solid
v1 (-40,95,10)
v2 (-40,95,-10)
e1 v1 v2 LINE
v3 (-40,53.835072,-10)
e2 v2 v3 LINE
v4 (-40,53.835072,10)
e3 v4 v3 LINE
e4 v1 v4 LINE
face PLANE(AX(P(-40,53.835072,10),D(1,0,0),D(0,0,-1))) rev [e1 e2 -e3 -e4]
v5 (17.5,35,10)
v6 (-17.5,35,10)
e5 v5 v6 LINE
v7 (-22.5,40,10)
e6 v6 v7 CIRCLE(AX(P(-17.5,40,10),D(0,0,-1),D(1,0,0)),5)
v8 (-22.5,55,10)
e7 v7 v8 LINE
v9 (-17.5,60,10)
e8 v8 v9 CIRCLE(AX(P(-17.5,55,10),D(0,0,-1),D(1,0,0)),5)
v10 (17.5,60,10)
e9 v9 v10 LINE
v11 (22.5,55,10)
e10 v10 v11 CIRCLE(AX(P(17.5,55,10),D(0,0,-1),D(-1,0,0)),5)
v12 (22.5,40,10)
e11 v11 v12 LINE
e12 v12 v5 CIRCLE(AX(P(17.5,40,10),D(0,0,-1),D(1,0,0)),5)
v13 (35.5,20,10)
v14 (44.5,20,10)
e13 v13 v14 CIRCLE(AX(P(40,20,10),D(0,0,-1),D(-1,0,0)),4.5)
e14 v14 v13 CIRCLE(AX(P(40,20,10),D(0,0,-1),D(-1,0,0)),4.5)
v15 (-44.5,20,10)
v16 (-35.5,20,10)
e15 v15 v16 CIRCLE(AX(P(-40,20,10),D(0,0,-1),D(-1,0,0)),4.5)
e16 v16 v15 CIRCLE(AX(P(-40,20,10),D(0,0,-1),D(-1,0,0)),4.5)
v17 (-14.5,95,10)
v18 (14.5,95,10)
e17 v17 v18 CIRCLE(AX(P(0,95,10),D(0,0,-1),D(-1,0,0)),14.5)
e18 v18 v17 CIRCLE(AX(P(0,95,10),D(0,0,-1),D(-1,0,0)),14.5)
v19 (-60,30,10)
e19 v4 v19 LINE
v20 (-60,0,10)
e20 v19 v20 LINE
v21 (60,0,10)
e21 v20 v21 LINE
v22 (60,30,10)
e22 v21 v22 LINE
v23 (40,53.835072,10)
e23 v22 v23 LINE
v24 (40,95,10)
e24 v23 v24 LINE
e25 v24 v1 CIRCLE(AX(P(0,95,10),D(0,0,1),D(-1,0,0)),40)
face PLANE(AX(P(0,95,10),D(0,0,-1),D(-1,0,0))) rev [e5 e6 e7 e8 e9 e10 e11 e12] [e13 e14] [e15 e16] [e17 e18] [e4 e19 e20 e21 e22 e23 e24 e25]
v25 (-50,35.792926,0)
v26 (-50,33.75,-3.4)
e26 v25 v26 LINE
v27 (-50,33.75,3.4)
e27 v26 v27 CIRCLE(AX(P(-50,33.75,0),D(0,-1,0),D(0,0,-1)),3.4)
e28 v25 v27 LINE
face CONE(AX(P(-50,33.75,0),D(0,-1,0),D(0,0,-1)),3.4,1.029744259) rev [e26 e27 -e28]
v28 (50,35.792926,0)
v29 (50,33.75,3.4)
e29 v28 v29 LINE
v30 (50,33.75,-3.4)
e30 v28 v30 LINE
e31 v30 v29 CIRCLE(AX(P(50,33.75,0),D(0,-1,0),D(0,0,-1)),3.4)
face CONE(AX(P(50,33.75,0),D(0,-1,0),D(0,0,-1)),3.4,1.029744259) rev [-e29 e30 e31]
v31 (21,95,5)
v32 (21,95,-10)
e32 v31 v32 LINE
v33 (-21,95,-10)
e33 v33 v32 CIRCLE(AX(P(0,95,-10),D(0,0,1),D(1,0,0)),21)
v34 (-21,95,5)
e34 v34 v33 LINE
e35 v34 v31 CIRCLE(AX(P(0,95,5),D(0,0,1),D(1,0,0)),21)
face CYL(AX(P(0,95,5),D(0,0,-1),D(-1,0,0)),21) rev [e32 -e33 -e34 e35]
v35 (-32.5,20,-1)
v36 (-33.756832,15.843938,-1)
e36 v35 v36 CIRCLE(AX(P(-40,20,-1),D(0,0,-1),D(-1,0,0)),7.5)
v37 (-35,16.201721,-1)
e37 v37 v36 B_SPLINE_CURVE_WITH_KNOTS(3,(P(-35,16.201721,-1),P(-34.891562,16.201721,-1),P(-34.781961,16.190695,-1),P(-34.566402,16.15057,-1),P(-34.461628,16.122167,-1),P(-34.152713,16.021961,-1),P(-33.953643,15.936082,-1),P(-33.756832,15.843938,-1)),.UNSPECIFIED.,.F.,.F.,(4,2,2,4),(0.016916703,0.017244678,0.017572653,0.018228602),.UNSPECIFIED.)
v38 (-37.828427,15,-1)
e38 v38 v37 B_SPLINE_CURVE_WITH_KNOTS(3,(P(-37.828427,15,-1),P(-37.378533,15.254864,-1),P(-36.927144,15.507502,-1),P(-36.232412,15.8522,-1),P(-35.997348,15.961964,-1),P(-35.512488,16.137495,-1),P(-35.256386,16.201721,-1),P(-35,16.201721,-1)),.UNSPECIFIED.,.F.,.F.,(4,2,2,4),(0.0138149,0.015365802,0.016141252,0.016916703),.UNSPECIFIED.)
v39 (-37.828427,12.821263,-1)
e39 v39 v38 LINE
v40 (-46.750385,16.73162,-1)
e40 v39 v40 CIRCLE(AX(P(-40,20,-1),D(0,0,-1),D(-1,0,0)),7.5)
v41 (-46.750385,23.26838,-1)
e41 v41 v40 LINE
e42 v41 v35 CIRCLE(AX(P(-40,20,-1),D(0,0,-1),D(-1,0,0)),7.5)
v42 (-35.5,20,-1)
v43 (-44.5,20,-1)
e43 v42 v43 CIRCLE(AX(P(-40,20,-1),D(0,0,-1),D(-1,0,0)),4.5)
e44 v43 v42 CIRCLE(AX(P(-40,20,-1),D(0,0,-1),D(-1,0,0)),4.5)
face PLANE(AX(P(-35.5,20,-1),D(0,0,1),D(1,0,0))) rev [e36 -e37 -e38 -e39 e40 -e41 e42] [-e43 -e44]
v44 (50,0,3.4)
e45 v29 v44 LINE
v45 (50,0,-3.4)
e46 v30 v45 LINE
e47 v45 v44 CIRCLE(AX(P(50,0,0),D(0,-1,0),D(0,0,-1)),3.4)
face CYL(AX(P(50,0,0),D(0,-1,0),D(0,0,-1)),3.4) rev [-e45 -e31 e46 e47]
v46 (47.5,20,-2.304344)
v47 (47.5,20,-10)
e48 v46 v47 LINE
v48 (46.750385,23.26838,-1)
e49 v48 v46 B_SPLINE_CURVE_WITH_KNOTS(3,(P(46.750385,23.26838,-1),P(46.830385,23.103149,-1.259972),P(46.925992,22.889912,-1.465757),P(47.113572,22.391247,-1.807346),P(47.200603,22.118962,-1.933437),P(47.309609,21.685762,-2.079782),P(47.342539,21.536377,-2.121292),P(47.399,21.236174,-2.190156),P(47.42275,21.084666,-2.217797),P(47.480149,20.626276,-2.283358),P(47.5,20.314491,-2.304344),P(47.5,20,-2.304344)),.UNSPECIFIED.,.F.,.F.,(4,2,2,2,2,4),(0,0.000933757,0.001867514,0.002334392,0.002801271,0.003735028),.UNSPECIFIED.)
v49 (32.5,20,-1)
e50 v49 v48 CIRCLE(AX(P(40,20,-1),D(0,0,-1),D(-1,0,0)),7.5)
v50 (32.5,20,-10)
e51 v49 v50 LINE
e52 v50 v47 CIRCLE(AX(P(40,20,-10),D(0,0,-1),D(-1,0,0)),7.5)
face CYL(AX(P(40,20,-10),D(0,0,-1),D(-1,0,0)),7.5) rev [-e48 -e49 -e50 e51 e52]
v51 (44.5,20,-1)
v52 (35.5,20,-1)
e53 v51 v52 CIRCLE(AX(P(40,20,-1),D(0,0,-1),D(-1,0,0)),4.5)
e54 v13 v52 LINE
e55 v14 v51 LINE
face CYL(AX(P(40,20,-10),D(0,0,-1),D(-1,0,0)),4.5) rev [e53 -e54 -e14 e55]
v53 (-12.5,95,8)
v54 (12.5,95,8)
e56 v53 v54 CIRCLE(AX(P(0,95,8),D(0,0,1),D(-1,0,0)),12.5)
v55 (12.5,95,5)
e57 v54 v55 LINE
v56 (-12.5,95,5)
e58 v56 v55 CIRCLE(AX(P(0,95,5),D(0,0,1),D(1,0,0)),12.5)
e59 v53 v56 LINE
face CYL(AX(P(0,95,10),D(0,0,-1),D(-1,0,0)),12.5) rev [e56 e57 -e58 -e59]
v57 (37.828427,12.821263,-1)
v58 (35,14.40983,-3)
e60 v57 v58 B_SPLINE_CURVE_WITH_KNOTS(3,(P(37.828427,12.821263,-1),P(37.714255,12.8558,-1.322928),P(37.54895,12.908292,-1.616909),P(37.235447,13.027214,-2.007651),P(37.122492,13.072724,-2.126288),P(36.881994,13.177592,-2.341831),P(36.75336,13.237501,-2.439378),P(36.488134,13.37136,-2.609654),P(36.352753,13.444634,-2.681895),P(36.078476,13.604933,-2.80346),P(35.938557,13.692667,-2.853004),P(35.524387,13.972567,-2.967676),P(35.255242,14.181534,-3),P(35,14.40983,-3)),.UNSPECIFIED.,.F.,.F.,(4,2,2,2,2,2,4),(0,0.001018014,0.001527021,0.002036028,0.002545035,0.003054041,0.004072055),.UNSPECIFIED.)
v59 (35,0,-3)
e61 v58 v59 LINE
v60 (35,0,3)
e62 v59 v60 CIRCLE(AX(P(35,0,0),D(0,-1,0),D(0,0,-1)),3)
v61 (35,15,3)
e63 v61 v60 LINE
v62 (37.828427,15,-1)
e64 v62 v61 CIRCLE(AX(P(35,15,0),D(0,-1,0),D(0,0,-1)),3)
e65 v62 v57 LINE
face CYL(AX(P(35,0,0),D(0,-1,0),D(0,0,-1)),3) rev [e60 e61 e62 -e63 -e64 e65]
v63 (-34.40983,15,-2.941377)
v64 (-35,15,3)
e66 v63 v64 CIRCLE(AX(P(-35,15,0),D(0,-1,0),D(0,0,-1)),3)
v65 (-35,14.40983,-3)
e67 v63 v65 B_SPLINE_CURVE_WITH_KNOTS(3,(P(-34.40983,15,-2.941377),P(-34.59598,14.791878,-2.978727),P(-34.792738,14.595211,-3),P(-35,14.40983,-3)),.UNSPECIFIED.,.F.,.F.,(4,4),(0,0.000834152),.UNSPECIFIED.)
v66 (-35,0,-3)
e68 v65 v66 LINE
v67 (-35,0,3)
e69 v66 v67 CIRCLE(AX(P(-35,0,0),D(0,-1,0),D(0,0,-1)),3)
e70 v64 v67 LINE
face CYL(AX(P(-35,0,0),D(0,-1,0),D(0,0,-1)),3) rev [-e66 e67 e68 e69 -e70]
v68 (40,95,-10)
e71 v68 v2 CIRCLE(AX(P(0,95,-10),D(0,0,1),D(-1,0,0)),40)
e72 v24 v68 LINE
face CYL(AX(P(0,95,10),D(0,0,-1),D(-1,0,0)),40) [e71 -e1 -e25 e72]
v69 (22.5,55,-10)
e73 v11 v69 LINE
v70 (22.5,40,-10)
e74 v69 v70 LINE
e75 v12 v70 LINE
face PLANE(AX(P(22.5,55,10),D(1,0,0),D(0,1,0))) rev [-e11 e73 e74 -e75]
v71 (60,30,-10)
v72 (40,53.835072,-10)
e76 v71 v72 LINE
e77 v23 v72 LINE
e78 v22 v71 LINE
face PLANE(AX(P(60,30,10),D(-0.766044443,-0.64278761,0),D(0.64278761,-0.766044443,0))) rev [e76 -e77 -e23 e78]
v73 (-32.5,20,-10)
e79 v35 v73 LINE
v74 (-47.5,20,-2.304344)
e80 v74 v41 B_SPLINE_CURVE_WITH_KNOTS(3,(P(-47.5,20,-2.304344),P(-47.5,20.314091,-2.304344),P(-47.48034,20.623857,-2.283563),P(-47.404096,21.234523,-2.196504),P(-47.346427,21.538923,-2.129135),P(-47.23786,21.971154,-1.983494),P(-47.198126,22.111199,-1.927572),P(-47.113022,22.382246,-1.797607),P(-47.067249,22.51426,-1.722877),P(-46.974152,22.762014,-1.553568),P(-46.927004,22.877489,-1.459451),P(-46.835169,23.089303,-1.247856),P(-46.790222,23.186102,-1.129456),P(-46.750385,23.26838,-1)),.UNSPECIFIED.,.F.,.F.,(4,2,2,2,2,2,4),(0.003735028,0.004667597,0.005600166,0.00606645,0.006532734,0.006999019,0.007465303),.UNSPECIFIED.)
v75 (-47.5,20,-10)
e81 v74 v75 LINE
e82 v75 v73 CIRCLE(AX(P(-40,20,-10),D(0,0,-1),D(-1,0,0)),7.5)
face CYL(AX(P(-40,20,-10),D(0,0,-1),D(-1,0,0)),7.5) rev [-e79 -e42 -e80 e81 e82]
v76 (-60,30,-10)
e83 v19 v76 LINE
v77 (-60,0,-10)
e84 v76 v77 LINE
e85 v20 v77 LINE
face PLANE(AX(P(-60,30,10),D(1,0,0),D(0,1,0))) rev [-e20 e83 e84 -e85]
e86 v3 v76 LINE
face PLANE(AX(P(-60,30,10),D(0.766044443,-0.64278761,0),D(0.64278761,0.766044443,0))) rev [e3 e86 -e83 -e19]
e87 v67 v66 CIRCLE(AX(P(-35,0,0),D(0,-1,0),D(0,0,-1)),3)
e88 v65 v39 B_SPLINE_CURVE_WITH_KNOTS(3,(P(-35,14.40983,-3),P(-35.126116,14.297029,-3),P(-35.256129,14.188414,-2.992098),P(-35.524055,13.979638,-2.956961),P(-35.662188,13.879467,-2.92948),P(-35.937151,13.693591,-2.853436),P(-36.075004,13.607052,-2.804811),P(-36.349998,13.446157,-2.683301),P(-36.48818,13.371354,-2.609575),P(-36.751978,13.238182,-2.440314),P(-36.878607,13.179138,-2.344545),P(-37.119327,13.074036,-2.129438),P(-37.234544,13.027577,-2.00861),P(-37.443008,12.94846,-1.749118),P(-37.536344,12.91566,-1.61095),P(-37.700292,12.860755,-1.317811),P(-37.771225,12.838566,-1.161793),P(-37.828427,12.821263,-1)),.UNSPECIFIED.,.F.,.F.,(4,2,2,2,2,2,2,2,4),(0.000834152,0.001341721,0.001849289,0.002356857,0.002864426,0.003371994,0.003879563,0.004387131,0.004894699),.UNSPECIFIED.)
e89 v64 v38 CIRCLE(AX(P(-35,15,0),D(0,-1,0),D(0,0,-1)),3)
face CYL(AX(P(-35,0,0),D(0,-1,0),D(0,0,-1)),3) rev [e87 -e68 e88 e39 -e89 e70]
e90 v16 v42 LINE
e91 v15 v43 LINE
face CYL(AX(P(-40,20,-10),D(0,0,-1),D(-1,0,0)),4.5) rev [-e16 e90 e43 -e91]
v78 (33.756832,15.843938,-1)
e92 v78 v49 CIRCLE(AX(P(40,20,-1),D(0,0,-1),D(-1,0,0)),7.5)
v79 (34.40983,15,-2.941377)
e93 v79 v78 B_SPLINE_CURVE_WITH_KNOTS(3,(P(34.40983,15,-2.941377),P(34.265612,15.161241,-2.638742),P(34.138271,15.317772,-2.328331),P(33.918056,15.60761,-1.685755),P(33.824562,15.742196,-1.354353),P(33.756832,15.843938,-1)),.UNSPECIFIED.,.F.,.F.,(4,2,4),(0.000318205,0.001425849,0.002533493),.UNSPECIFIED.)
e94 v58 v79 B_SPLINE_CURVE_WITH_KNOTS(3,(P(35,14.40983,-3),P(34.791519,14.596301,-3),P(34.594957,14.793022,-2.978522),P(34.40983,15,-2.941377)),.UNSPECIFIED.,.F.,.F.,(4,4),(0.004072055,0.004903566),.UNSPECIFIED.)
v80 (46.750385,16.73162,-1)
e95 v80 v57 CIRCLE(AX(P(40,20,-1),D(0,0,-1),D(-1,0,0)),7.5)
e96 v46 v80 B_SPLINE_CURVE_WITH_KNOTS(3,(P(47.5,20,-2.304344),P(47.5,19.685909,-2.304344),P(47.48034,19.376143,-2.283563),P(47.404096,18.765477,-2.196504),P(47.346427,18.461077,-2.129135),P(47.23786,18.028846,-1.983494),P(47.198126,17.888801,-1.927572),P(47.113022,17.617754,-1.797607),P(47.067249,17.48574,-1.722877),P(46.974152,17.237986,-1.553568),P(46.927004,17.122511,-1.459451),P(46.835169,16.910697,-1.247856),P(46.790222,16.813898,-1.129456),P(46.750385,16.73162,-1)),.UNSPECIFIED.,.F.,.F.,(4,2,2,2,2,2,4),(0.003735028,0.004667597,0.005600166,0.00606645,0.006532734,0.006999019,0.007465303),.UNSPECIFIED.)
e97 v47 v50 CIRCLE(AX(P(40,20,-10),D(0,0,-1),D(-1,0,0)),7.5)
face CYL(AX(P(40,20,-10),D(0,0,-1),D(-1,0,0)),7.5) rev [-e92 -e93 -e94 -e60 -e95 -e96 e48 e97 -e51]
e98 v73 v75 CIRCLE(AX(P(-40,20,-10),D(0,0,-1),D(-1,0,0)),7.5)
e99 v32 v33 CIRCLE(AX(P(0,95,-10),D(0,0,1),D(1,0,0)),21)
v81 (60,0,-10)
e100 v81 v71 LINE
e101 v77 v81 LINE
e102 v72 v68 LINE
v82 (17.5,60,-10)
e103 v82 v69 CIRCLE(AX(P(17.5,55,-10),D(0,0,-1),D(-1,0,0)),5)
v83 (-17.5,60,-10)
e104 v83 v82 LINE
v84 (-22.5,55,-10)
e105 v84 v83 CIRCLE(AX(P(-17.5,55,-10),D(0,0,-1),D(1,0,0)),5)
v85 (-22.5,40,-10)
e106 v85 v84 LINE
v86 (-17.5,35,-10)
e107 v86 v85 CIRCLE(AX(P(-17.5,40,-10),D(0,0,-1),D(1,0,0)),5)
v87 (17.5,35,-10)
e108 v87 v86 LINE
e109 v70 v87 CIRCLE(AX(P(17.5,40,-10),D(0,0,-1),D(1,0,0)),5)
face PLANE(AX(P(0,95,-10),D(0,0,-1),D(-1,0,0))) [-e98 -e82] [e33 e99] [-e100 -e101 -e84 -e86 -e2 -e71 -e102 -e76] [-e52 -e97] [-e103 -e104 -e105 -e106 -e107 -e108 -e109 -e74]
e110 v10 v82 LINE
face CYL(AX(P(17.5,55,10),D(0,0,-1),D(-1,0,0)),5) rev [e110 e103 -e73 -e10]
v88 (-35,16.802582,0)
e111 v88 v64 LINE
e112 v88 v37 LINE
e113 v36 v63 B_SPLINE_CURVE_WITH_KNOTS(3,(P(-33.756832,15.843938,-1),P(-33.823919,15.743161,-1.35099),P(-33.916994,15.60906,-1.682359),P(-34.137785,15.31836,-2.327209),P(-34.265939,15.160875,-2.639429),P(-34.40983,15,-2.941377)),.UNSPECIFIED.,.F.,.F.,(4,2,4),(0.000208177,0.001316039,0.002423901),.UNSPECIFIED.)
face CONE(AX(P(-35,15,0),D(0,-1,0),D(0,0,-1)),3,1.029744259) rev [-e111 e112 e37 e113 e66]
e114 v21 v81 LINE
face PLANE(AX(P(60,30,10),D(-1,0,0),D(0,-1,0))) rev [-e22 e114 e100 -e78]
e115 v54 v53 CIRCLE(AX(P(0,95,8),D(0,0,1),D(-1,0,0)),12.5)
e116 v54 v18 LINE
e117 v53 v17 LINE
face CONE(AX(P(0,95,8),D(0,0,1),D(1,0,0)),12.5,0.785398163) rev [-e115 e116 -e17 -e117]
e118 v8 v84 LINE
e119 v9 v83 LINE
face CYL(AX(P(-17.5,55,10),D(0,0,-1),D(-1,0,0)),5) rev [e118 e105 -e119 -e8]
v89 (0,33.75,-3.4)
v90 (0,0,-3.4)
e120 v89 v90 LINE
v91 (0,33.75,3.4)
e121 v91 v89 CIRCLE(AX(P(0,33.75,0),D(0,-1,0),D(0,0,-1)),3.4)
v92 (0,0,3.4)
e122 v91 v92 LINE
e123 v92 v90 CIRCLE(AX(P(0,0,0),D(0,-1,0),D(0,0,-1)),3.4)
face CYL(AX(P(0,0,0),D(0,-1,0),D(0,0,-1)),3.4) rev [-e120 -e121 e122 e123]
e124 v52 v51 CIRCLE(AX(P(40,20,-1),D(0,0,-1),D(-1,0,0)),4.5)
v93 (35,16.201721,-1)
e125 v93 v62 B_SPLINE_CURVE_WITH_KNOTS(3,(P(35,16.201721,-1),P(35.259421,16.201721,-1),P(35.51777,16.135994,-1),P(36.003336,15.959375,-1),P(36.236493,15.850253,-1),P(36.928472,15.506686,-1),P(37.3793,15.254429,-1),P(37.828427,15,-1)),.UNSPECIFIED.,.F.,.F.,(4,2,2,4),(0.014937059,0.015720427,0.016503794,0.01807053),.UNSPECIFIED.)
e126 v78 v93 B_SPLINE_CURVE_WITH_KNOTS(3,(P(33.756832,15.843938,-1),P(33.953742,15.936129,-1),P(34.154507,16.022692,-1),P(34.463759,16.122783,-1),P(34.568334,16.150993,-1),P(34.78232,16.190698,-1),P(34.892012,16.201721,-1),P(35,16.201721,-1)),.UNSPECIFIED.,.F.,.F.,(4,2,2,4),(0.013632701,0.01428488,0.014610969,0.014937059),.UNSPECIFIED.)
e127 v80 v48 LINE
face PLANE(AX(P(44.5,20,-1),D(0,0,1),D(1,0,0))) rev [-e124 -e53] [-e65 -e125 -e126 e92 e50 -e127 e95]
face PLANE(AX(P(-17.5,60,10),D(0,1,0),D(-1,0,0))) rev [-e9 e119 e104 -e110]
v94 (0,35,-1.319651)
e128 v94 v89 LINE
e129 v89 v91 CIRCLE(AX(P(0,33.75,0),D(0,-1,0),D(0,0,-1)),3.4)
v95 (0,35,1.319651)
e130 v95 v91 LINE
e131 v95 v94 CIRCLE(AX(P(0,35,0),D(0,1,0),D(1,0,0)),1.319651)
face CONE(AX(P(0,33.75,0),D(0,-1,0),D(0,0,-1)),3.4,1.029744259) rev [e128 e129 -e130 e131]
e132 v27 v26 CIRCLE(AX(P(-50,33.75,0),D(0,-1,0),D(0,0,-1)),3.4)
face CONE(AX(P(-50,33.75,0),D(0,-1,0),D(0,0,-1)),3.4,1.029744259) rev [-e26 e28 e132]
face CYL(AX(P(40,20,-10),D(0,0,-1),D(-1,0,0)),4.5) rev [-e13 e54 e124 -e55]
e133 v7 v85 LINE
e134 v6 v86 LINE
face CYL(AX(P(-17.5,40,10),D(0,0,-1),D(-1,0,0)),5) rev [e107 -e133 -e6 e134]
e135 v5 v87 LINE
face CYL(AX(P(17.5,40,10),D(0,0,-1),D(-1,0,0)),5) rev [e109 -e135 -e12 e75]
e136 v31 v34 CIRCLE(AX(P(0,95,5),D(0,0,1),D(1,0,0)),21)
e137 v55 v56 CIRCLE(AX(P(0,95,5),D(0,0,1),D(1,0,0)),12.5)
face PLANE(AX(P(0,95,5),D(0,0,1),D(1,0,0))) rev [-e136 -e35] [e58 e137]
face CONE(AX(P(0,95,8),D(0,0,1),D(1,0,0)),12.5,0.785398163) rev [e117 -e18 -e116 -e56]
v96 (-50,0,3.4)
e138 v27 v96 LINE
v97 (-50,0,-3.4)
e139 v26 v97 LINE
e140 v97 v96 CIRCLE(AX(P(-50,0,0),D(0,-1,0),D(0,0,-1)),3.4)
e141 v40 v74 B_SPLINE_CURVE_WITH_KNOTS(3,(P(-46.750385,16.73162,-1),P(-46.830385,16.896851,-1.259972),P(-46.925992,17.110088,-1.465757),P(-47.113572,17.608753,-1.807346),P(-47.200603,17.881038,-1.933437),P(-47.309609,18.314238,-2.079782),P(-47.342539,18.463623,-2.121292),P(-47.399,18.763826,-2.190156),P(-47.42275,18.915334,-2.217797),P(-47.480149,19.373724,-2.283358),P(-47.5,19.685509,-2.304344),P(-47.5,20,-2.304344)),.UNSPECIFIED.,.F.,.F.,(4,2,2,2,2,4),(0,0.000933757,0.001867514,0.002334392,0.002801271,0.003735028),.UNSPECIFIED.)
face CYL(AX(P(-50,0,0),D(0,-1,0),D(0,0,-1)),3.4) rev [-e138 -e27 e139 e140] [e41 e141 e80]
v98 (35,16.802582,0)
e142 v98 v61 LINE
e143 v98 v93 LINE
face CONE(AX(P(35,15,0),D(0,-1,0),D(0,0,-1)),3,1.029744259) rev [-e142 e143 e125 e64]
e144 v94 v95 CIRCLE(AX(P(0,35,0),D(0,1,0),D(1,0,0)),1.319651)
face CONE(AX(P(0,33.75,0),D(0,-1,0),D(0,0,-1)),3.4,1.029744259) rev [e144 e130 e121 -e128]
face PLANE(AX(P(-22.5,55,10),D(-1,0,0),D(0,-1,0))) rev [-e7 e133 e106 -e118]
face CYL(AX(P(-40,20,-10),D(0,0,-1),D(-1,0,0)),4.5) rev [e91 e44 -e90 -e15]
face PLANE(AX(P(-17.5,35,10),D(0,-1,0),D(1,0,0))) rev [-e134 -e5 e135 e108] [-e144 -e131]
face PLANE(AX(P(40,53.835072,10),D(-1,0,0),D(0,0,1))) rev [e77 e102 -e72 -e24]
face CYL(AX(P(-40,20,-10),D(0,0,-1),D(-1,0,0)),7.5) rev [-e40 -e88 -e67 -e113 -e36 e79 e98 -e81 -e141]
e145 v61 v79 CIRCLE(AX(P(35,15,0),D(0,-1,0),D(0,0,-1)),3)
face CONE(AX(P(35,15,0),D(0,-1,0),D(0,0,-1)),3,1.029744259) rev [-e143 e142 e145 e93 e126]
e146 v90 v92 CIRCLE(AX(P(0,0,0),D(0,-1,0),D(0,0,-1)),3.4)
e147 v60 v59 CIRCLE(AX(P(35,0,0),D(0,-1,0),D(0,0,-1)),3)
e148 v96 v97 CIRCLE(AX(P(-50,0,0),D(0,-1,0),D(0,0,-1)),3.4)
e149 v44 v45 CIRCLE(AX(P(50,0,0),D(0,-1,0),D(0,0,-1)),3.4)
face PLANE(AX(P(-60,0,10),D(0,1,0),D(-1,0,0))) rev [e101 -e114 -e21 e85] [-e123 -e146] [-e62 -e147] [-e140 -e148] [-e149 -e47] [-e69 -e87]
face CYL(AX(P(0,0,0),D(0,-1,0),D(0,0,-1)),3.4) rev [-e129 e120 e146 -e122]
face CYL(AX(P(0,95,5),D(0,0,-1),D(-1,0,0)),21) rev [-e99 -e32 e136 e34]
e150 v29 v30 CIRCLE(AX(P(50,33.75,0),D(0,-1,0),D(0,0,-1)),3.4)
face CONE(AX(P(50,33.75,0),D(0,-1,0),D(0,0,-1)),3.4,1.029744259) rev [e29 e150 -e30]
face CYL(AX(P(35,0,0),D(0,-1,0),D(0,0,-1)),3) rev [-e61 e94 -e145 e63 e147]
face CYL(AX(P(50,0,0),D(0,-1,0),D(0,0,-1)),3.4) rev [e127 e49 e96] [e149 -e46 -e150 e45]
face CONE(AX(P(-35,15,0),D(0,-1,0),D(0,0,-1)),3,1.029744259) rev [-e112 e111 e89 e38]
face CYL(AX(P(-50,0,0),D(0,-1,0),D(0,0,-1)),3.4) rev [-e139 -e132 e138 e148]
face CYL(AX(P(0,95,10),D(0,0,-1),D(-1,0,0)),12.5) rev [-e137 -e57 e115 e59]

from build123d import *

# Parameters (mm, degrees)
SKETCH_1_R                = 12.5
EXTRUDE_1_DEPTH           = 10
HOLE_WIZARD_M8_1_D        = 6.8
HOLE_WIZARD_M8_1_DEPTH    = 33.75
HOLE_WIZARD_M8_1_TIP      = 2.042926105
HOLE_WIZARD_6_0_6_1_D     = 6
HOLE_WIZARD_6_0_6_1_DEPTH = 15
HOLE_WIZARD_6_0_6_1_TIP   = 1.802581857
SKETCH_6_R                = 21
CUT_EXTRUDE_1_DEPTH       = 15
CHAMFER_1_SIZE            = 2
HOLE_WIZARD_2_D           = 9
HOLE_WIZARD_2_CBORE_D     = 15
HOLE_WIZARD_2_CBORE_DEPTH = 9
CUT_EXTRUDE_2_DEPTH       = 150.080515159


with BuildPart() as part:
    # 草图1 → 凸台-拉伸1 (new, symmetric)
    with BuildSketch(Plane.XY):
        with BuildLine():
            Line((-60, 30), (-40, 53.835071852))
            Line((-40, 53.835071852), (-40, 95))
            ThreePointArc((-40, 95), (0, 135), (40, 95))
            Line((40, 95), (40, 53.835071852))
            Line((40, 53.835071852), (60, 30))
            Line((60, 30), (60, 0))
            Line((60, 0), (-60, 0))
            Line((-60, 0), (-60, 30))
        make_face()
        with Locations((0, 95)):
            Circle(SKETCH_1_R, mode=Mode.SUBTRACT)
    extrude(amount=EXTRUDE_1_DEPTH, both=True)

    # M8 螺纹孔1
    with Locations(Plane(origin=(0, 0, 0), x_dir=(-1, 0, 0), z_dir=(0, -1, 0))):
        with Locations((50, 0), (0, 0), (-50, 0)):
            Hole(HOLE_WIZARD_M8_1_D / 2, depth=HOLE_WIZARD_M8_1_DEPTH)
            with Locations((0, 0, -(HOLE_WIZARD_M8_1_DEPTH + HOLE_WIZARD_M8_1_TIP / 2))):  # 118° drill point
                Cone(0, HOLE_WIZARD_M8_1_D / 2, HOLE_WIZARD_M8_1_TIP, mode=Mode.SUBTRACT)

    # Ø6.0 (6) 直径孔1
    with Locations(Plane(origin=(0, 0, 0), x_dir=(-1, 0, 0), z_dir=(0, -1, 0))):
        with Locations((-35, 0), (35, 0)):
            Hole(HOLE_WIZARD_6_0_6_1_D / 2, depth=HOLE_WIZARD_6_0_6_1_DEPTH)
            with Locations((0, 0, -(HOLE_WIZARD_6_0_6_1_DEPTH + HOLE_WIZARD_6_0_6_1_TIP / 2))):  # 118° drill point
                Cone(0, HOLE_WIZARD_6_0_6_1_D / 2, HOLE_WIZARD_6_0_6_1_TIP, mode=Mode.SUBTRACT)

    # 草图6 → 切除-拉伸1 (cut)
    with BuildSketch(Plane.XY.offset(-10)):
        with Locations((0, 95)):
            Circle(SKETCH_6_R)
    extrude(amount=CUT_EXTRUDE_1_DEPTH, mode=Mode.SUBTRACT)

    # 倒角1
    chamfer_1_edges = [part.edges().sort_by_distance(p)[0] for p in [
        (-12.5, 95, 10),
    ]]
    chamfer(chamfer_1_edges, length=CHAMFER_1_SIZE)

    # 打孔尺寸(%根据)内六角圆柱头螺钉的类型2 (through all)
    with Locations(Plane(origin=(0, 0, -10), x_dir=(-1, 0, 0), z_dir=(0, 0, -1))):
        with Locations((-40, 20), (40, 20)):
            CounterBoreHole(HOLE_WIZARD_2_D / 2, HOLE_WIZARD_2_CBORE_D / 2, HOLE_WIZARD_2_CBORE_DEPTH)

    # 草图13 → 切除-拉伸2 (cut, through all)
    with BuildSketch(Plane(origin=(0, 0, -10), x_dir=(-1, 0, 0), z_dir=(0, 0, -1))):
        with BuildLine():
            Line((17.5, 60), (-17.5, 60))
            ThreePointArc((-17.5, 60), (-21.035533906, 58.535533906), (-22.5, 55))
            Line((-22.5, 55), (-22.5, 40))
            ThreePointArc((-22.5, 40), (-21.035533906, 36.464466094), (-17.5, 35))
            Line((-17.5, 35), (17.5, 35))
            ThreePointArc((17.5, 35), (21.035533906, 36.464466094), (22.5, 40))
            Line((22.5, 40), (22.5, 55))
            ThreePointArc((22.5, 55), (21.035533906, 58.535533906), (17.5, 60))
        make_face()
    extrude(amount=-CUT_EXTRUDE_2_DEPTH, mode=Mode.SUBTRACT)


solid = part.part
